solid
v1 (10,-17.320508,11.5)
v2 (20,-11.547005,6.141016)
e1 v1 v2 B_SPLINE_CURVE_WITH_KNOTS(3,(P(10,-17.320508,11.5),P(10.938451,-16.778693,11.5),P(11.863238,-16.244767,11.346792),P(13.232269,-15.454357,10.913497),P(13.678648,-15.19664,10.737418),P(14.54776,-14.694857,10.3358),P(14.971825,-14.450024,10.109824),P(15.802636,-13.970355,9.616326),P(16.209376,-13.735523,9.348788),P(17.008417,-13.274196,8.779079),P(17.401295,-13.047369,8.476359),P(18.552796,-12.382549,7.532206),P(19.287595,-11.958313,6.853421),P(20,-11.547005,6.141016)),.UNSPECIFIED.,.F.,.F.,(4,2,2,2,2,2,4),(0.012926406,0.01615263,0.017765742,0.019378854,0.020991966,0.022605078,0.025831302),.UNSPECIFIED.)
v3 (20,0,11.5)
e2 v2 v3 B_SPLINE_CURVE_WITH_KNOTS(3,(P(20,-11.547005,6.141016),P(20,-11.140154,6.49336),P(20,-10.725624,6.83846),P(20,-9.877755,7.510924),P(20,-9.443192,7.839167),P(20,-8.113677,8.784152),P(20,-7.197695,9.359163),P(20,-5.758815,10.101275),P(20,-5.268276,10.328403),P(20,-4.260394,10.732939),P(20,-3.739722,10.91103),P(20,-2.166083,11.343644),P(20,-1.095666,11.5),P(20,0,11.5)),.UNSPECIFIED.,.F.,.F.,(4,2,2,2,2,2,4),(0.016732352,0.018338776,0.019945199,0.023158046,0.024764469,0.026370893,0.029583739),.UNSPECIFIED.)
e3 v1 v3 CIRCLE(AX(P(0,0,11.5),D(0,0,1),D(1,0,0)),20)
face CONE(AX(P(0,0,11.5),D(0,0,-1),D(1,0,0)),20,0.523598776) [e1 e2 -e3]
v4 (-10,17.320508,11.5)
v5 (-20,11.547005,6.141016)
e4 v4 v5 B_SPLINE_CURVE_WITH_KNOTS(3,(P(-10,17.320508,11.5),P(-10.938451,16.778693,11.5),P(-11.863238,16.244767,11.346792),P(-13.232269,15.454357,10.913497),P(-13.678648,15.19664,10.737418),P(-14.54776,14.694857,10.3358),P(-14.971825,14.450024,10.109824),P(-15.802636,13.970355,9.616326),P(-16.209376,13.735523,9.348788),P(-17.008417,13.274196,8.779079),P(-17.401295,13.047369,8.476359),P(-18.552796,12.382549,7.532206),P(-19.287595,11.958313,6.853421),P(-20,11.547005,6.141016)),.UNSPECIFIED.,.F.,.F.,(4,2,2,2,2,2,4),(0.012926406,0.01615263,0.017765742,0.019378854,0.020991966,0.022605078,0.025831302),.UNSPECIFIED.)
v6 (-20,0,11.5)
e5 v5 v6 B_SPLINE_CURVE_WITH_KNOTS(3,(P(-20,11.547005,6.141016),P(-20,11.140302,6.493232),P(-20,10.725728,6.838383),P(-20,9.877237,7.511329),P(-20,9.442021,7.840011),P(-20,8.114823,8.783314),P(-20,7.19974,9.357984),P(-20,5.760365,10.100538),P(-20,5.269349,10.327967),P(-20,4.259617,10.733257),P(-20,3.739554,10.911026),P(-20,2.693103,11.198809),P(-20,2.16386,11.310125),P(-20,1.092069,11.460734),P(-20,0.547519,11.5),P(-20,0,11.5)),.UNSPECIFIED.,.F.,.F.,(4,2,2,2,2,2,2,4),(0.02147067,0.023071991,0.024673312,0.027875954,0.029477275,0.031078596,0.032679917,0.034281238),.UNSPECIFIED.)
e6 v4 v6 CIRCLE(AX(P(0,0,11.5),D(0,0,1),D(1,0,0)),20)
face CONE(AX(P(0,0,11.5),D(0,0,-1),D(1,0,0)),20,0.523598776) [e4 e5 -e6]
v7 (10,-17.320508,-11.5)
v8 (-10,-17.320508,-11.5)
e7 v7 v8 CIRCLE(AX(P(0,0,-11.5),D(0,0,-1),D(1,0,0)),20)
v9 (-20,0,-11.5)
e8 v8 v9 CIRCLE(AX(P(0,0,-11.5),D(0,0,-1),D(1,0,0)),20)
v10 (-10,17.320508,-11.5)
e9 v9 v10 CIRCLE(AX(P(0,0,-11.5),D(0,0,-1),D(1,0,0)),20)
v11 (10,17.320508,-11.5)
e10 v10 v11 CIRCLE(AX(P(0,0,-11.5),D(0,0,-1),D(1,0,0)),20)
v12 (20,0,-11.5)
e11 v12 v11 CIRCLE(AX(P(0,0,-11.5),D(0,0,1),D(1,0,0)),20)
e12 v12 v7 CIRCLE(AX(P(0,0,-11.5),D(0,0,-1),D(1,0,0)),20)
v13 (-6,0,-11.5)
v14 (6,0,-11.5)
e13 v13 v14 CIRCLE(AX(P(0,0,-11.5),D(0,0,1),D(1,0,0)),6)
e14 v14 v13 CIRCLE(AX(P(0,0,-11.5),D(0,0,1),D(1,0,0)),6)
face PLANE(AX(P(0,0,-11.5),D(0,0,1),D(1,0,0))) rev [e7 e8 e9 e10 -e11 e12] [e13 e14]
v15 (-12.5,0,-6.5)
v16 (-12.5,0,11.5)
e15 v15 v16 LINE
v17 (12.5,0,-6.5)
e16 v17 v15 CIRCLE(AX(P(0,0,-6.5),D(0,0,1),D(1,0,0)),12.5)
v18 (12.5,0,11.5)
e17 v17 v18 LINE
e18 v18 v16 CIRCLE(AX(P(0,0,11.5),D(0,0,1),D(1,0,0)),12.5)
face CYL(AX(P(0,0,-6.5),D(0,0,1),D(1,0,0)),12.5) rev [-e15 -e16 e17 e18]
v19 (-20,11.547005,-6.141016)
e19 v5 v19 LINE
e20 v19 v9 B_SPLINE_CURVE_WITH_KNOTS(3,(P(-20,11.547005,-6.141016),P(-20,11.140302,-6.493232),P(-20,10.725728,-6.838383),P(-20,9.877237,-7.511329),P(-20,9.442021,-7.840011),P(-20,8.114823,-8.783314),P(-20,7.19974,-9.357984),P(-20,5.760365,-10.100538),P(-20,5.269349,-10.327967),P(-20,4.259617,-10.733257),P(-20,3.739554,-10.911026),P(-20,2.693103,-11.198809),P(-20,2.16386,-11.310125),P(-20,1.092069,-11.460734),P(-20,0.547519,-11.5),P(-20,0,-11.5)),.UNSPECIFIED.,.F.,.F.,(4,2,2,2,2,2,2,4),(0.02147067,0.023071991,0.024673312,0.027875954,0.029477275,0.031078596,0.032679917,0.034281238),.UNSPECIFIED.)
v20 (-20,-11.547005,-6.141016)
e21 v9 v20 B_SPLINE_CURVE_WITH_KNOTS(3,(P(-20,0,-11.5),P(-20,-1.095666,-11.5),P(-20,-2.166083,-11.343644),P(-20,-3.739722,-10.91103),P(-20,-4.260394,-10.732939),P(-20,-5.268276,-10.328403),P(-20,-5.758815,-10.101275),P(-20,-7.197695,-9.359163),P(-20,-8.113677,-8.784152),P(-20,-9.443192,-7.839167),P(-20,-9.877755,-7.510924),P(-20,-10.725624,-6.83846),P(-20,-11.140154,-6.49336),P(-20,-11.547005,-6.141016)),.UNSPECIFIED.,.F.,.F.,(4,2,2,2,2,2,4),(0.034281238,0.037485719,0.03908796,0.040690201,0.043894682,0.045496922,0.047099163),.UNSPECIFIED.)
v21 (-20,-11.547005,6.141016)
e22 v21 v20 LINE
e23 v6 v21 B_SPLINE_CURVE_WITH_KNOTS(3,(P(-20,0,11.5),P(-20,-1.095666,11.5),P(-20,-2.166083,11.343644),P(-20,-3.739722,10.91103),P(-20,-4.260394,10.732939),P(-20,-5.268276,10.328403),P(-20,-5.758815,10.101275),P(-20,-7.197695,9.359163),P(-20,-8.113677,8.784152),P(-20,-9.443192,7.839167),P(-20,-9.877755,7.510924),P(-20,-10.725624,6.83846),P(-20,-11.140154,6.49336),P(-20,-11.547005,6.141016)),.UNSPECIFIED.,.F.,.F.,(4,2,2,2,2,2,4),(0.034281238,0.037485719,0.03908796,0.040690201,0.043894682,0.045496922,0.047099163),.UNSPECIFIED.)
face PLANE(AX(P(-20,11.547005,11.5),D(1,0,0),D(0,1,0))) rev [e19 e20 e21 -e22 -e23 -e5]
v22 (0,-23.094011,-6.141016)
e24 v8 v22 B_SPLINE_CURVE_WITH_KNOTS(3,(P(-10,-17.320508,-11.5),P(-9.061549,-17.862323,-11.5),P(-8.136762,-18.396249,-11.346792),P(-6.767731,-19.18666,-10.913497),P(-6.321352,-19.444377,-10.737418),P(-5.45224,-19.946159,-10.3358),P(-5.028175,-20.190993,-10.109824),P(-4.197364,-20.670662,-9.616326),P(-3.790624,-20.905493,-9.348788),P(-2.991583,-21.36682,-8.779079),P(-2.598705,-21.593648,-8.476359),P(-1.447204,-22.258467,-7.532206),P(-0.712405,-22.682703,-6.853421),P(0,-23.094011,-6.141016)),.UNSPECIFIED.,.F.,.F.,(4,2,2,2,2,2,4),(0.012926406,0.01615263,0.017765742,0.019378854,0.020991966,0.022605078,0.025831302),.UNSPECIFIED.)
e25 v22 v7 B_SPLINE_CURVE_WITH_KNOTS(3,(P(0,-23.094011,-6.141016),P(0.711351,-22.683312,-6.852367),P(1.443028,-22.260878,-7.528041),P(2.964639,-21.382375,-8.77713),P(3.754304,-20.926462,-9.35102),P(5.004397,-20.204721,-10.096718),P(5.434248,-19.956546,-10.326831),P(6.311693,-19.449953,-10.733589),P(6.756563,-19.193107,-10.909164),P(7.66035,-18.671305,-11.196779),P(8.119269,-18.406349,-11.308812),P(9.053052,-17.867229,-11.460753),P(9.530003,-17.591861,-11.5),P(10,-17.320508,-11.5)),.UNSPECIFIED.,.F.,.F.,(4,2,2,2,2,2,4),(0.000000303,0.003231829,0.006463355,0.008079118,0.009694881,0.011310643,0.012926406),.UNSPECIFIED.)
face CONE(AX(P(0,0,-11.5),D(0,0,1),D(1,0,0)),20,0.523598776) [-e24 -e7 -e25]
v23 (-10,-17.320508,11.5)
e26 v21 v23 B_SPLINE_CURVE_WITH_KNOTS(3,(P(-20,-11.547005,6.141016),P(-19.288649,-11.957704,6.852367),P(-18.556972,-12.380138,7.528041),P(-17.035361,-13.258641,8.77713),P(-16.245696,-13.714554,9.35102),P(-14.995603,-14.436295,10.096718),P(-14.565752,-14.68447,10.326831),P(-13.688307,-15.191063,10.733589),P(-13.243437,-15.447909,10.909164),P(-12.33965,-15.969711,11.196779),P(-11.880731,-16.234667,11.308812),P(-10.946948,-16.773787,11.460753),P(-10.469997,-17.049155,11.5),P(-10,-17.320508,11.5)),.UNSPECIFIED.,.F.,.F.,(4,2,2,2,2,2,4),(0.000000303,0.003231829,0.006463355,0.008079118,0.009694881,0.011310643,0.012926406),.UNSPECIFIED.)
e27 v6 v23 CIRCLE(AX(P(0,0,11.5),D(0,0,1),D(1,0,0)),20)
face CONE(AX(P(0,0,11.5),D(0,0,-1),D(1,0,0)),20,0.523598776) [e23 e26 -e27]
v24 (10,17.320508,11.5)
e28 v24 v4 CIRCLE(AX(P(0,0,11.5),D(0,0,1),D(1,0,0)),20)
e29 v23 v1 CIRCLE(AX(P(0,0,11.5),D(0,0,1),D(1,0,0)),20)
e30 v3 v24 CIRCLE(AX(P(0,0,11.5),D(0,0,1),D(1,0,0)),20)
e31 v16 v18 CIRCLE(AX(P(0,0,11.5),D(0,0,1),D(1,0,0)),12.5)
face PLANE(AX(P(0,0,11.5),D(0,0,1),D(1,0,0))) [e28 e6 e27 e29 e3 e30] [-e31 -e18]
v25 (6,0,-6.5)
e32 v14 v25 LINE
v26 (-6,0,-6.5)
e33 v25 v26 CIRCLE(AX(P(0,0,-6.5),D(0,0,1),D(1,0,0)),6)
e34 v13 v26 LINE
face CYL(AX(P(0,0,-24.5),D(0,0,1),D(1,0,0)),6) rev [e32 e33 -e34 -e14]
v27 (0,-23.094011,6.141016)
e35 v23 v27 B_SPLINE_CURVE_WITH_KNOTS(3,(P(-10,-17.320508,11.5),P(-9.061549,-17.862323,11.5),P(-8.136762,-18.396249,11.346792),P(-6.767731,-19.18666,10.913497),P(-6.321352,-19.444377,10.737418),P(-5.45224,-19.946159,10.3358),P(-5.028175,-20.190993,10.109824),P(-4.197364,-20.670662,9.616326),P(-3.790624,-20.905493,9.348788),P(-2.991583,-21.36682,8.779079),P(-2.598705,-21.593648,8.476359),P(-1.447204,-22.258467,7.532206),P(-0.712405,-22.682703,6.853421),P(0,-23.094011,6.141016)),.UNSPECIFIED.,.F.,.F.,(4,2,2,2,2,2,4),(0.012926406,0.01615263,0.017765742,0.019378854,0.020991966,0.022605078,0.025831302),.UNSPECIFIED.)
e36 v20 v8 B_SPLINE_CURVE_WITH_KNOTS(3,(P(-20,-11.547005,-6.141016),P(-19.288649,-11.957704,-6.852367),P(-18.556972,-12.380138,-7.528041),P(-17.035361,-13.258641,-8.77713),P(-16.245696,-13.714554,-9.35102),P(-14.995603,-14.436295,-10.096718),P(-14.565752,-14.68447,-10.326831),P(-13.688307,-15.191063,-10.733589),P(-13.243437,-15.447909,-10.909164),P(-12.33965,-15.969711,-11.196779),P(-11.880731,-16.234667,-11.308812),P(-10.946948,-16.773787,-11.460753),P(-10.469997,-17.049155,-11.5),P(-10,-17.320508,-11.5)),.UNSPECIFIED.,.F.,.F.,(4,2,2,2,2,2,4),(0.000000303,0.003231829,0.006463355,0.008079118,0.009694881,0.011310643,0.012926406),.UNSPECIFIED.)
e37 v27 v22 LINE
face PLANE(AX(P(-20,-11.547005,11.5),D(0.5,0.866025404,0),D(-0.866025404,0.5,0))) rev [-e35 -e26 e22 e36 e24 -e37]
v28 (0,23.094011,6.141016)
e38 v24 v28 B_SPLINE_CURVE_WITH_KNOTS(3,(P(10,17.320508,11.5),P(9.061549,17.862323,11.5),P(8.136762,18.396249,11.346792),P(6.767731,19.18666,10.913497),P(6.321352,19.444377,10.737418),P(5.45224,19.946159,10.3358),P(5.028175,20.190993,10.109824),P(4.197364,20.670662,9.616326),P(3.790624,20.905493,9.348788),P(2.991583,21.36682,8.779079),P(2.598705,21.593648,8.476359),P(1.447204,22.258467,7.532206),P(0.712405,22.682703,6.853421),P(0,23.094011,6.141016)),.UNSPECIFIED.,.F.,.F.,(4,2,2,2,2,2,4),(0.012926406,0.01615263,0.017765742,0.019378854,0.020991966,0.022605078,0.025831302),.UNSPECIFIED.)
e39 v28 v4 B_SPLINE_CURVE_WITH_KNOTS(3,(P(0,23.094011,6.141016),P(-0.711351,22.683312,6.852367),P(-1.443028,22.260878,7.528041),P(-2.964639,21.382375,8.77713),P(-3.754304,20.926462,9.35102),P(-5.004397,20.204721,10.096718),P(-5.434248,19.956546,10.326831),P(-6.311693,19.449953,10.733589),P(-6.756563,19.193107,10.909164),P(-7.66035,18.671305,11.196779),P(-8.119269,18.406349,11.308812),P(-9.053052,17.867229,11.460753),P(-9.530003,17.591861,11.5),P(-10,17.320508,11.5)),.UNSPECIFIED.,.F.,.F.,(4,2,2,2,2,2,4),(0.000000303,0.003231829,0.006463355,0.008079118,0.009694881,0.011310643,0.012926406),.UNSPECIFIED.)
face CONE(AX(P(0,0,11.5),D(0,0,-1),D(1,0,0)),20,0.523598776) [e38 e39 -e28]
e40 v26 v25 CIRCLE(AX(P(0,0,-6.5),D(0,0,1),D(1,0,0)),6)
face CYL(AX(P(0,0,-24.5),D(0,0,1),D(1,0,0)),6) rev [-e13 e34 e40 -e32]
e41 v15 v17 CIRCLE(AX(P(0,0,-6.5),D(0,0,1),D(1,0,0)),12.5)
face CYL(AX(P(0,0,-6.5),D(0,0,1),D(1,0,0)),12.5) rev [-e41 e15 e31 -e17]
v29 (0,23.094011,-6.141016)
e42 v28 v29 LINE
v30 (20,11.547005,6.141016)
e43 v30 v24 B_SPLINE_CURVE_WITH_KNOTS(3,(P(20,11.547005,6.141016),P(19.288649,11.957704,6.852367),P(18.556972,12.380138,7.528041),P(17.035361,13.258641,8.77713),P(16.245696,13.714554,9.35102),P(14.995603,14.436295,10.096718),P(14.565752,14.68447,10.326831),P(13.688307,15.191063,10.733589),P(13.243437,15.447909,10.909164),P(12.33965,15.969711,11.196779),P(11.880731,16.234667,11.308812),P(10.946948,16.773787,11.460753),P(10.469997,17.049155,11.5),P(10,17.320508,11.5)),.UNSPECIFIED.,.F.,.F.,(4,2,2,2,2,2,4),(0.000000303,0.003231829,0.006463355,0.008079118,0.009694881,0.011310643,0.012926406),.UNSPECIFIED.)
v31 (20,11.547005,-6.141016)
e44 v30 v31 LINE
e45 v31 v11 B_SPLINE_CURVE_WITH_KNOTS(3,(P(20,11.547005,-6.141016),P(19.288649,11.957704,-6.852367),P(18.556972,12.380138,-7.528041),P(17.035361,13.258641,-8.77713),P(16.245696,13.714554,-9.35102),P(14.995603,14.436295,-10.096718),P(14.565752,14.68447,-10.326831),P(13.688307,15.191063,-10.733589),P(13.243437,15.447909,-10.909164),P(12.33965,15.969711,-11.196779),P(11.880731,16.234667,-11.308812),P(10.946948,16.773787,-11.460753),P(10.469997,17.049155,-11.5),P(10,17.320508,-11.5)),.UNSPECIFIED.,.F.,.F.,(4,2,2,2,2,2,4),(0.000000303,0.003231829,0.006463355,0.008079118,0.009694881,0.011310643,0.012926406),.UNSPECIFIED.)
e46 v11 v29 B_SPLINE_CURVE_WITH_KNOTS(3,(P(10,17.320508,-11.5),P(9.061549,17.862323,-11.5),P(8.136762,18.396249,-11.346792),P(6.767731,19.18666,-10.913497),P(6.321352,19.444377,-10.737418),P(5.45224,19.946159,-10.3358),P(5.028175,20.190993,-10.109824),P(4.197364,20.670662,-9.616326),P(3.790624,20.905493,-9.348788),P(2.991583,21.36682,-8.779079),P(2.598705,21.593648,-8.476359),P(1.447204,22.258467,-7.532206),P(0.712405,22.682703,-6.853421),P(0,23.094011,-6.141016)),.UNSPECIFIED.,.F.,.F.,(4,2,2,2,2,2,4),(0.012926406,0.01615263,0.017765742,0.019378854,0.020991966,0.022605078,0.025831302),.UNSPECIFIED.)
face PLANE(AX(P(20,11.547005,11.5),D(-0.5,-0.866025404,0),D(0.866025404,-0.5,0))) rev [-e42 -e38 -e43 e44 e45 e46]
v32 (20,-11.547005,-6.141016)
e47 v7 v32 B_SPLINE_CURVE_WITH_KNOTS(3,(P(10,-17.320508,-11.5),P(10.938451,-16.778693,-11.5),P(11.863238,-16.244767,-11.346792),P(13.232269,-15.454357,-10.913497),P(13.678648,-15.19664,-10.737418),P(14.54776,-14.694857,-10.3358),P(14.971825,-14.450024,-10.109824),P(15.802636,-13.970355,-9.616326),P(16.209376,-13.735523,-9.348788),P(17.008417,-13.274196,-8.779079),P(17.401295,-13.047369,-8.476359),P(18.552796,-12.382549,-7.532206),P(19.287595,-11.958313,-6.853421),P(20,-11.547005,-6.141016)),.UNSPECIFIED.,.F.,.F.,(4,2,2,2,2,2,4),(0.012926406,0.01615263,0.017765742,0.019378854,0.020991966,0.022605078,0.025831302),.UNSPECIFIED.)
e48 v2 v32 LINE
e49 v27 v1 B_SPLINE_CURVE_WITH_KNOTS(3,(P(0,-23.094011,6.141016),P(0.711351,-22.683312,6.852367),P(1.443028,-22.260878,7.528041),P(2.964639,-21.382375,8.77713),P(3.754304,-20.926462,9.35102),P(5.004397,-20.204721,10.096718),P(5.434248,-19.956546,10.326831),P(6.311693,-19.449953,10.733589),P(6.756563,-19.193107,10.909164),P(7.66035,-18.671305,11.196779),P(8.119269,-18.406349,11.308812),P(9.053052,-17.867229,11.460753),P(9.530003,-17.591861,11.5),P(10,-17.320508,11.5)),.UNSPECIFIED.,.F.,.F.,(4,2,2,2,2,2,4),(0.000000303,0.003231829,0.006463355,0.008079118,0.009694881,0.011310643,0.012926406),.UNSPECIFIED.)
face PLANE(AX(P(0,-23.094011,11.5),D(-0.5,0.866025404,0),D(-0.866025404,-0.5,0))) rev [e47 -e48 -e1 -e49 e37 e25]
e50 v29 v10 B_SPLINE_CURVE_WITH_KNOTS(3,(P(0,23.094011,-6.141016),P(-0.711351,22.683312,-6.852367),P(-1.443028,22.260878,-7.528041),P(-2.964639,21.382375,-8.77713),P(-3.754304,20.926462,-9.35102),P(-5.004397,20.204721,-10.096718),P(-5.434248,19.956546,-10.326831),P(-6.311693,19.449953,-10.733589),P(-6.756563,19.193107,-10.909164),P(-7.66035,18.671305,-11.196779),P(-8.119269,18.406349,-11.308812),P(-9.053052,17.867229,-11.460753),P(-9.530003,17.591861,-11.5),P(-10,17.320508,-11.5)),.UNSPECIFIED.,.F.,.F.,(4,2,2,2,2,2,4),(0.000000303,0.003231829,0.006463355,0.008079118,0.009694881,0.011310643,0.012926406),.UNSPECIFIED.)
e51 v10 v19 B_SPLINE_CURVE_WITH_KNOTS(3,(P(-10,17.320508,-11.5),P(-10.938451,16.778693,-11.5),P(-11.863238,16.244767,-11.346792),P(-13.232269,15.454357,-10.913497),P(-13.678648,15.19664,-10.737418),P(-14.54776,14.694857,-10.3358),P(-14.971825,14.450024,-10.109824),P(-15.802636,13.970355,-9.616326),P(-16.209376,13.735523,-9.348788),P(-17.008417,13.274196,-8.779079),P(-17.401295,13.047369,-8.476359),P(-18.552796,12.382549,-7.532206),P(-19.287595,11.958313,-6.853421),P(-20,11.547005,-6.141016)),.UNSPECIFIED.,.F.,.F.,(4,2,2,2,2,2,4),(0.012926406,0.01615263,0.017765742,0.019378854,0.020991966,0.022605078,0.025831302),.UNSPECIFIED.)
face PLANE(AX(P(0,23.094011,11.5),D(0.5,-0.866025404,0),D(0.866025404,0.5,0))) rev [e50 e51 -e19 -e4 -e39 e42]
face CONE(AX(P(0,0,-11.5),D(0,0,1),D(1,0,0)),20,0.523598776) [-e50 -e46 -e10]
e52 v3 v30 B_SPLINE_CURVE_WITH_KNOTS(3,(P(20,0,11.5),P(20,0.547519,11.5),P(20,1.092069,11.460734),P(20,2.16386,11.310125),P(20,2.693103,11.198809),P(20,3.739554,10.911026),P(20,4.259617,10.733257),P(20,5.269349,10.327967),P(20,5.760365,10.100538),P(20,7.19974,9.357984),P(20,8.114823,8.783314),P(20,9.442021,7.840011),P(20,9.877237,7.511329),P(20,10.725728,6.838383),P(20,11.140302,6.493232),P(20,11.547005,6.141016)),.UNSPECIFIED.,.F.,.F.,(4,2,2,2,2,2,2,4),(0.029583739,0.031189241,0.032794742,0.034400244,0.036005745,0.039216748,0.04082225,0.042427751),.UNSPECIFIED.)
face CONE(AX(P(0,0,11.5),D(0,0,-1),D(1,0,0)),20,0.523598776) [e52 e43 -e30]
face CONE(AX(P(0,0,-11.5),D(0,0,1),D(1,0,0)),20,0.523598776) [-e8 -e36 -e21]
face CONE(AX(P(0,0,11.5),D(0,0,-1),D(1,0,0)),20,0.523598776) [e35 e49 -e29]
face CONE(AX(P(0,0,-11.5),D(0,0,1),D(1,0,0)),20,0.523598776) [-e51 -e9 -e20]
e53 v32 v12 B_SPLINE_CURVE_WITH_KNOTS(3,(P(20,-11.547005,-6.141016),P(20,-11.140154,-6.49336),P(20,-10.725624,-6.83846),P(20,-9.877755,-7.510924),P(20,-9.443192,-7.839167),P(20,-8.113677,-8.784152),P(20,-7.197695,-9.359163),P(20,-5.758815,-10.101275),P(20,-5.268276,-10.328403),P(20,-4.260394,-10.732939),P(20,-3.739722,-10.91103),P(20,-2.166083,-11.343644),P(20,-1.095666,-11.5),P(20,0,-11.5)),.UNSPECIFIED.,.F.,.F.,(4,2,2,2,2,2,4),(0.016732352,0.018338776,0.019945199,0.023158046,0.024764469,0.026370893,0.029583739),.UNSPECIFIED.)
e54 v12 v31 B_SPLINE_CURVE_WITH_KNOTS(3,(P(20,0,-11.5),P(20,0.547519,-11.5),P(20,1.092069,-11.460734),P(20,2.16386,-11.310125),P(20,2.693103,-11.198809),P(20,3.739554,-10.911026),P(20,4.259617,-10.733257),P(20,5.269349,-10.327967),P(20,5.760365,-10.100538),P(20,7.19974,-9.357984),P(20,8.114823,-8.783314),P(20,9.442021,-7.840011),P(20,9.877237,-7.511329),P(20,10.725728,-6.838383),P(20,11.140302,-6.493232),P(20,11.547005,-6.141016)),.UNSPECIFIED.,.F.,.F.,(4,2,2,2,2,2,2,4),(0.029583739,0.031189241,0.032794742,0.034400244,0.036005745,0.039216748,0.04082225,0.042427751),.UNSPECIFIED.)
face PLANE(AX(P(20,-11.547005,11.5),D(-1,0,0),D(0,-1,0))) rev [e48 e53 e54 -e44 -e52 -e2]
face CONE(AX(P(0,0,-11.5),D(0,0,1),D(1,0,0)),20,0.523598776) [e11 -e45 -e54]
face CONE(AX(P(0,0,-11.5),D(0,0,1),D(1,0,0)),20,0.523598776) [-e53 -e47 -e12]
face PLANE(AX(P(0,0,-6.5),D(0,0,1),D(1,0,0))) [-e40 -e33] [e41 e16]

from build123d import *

# Parameters (mm, degrees)
BOSS_EXTRUDE1_DEPTH     = 11.5
SKETCH2_OUTSIDE_W       = 75.842
SKETCH2_OUTSIDE_H       = 82.03
SKETCH2_OUTSIDE_R       = 20
CUT_EXTRUDE1_DEPTH      = 18
CUT_EXTRUDE1_DRAFT      = -30
MIRROR1_COPY_1_SKETCH_W = 75.842
MIRROR1_COPY_1_SKETCH_H = 82.03
MIRROR1_COPY_1_SKETCH_R = 20
MIRROR1_COPY_1_DEPTH    = 18
MIRROR1_COPY_1_DRAFT    = -30
SKETCH3_R               = 12.5
CUT_EXTRUDE2_DEPTH      = 18
SKETCH4_R               = 6
CUT_EXTRUDE3_DEPTH      = 18


with BuildPart() as part:
    # Sketch1 → Boss-Extrude1 (new, symmetric)
    with BuildSketch(Plane.XY):
        Polygon((0, 23.094010768), (-20, 11.547005384), (-20, -11.547005384), (0, -23.094010768), (20, -11.547005384), (20, 11.547005384), align=None)
    extrude(amount=BOSS_EXTRUDE1_DEPTH, both=True)


with BuildPart() as cut_extrude1_tool:
    # Sketch2 outside → Cut-Extrude1 (with draft: the straight prism first)
    with BuildSketch(Plane.XY.offset(11.5)):
        Rectangle(SKETCH2_OUTSIDE_W, SKETCH2_OUTSIDE_H)
        Circle(SKETCH2_OUTSIDE_R, mode=Mode.SUBTRACT)
    extrude(amount=-CUT_EXTRUDE1_DEPTH)
    # Cut-Extrude1: the draft: its side faces are tilted about the plane it starts from
    cut_extrude1_sides = [cut_extrude1_tool.faces().sort_by_distance(p)[0] for p in [
        (0, -41.015, 2.5),
        (37.921, 0, 2.5),
        (0, 41.015, 2.5),
        (-37.921, 0, 2.5),
        (-20, 0, 2.5),
    ]]
    draft(cut_extrude1_sides, Plane.XY.offset(11.5), CUT_EXTRUDE1_DRAFT)


with BuildPart() as part_1:
    add(part.part)

    # Cut-Extrude1: cut by cut_extrude1_tool
    add(cut_extrude1_tool.part, mode=Mode.SUBTRACT)


with BuildPart() as mirror1_copy_1_tool:
    # Mirror1 copy 1 sketch → Mirror1 copy 1 (with draft: the straight prism first)
    with BuildSketch(Plane(origin=(0, 0, -11.5), x_dir=(1, 0, 0), z_dir=(0, 0, -1))):
        Rectangle(MIRROR1_COPY_1_SKETCH_W, MIRROR1_COPY_1_SKETCH_H)
        Circle(MIRROR1_COPY_1_SKETCH_R, mode=Mode.SUBTRACT)
    extrude(amount=-MIRROR1_COPY_1_DEPTH)
    # Mirror1 copy 1: the draft: its side faces are tilted about the plane it starts from
    mirror1_copy_1_sides = [mirror1_copy_1_tool.faces().sort_by_distance(p)[0] for p in [
        (0, -41.015, -2.5),
        (37.921, 0, -2.5),
        (0, 41.015, -2.5),
        (-37.921, 0, -2.5),
        (-20, 0, -2.5),
    ]]
    draft(mirror1_copy_1_sides, Plane(origin=(0, 0, -11.5), x_dir=(1, 0, 0), z_dir=(0, 0, -1)), MIRROR1_COPY_1_DRAFT)


with BuildPart() as part_2:
    add(part_1.part)

    # Mirror1 copy 1: cut by mirror1_copy_1_tool
    add(mirror1_copy_1_tool.part, mode=Mode.SUBTRACT)

    # Sketch3 → Cut-Extrude2 (cut)
    with BuildSketch(Plane.XY.offset(11.5)):
        Circle(SKETCH3_R)
    extrude(amount=-CUT_EXTRUDE2_DEPTH, mode=Mode.SUBTRACT)

    # Sketch4 → Cut-Extrude3 (cut)
    with BuildSketch(Plane.XY.offset(-6.5)):
        Circle(SKETCH4_R)
    extrude(amount=-CUT_EXTRUDE3_DEPTH, mode=Mode.SUBTRACT)


solid = part_2.part
